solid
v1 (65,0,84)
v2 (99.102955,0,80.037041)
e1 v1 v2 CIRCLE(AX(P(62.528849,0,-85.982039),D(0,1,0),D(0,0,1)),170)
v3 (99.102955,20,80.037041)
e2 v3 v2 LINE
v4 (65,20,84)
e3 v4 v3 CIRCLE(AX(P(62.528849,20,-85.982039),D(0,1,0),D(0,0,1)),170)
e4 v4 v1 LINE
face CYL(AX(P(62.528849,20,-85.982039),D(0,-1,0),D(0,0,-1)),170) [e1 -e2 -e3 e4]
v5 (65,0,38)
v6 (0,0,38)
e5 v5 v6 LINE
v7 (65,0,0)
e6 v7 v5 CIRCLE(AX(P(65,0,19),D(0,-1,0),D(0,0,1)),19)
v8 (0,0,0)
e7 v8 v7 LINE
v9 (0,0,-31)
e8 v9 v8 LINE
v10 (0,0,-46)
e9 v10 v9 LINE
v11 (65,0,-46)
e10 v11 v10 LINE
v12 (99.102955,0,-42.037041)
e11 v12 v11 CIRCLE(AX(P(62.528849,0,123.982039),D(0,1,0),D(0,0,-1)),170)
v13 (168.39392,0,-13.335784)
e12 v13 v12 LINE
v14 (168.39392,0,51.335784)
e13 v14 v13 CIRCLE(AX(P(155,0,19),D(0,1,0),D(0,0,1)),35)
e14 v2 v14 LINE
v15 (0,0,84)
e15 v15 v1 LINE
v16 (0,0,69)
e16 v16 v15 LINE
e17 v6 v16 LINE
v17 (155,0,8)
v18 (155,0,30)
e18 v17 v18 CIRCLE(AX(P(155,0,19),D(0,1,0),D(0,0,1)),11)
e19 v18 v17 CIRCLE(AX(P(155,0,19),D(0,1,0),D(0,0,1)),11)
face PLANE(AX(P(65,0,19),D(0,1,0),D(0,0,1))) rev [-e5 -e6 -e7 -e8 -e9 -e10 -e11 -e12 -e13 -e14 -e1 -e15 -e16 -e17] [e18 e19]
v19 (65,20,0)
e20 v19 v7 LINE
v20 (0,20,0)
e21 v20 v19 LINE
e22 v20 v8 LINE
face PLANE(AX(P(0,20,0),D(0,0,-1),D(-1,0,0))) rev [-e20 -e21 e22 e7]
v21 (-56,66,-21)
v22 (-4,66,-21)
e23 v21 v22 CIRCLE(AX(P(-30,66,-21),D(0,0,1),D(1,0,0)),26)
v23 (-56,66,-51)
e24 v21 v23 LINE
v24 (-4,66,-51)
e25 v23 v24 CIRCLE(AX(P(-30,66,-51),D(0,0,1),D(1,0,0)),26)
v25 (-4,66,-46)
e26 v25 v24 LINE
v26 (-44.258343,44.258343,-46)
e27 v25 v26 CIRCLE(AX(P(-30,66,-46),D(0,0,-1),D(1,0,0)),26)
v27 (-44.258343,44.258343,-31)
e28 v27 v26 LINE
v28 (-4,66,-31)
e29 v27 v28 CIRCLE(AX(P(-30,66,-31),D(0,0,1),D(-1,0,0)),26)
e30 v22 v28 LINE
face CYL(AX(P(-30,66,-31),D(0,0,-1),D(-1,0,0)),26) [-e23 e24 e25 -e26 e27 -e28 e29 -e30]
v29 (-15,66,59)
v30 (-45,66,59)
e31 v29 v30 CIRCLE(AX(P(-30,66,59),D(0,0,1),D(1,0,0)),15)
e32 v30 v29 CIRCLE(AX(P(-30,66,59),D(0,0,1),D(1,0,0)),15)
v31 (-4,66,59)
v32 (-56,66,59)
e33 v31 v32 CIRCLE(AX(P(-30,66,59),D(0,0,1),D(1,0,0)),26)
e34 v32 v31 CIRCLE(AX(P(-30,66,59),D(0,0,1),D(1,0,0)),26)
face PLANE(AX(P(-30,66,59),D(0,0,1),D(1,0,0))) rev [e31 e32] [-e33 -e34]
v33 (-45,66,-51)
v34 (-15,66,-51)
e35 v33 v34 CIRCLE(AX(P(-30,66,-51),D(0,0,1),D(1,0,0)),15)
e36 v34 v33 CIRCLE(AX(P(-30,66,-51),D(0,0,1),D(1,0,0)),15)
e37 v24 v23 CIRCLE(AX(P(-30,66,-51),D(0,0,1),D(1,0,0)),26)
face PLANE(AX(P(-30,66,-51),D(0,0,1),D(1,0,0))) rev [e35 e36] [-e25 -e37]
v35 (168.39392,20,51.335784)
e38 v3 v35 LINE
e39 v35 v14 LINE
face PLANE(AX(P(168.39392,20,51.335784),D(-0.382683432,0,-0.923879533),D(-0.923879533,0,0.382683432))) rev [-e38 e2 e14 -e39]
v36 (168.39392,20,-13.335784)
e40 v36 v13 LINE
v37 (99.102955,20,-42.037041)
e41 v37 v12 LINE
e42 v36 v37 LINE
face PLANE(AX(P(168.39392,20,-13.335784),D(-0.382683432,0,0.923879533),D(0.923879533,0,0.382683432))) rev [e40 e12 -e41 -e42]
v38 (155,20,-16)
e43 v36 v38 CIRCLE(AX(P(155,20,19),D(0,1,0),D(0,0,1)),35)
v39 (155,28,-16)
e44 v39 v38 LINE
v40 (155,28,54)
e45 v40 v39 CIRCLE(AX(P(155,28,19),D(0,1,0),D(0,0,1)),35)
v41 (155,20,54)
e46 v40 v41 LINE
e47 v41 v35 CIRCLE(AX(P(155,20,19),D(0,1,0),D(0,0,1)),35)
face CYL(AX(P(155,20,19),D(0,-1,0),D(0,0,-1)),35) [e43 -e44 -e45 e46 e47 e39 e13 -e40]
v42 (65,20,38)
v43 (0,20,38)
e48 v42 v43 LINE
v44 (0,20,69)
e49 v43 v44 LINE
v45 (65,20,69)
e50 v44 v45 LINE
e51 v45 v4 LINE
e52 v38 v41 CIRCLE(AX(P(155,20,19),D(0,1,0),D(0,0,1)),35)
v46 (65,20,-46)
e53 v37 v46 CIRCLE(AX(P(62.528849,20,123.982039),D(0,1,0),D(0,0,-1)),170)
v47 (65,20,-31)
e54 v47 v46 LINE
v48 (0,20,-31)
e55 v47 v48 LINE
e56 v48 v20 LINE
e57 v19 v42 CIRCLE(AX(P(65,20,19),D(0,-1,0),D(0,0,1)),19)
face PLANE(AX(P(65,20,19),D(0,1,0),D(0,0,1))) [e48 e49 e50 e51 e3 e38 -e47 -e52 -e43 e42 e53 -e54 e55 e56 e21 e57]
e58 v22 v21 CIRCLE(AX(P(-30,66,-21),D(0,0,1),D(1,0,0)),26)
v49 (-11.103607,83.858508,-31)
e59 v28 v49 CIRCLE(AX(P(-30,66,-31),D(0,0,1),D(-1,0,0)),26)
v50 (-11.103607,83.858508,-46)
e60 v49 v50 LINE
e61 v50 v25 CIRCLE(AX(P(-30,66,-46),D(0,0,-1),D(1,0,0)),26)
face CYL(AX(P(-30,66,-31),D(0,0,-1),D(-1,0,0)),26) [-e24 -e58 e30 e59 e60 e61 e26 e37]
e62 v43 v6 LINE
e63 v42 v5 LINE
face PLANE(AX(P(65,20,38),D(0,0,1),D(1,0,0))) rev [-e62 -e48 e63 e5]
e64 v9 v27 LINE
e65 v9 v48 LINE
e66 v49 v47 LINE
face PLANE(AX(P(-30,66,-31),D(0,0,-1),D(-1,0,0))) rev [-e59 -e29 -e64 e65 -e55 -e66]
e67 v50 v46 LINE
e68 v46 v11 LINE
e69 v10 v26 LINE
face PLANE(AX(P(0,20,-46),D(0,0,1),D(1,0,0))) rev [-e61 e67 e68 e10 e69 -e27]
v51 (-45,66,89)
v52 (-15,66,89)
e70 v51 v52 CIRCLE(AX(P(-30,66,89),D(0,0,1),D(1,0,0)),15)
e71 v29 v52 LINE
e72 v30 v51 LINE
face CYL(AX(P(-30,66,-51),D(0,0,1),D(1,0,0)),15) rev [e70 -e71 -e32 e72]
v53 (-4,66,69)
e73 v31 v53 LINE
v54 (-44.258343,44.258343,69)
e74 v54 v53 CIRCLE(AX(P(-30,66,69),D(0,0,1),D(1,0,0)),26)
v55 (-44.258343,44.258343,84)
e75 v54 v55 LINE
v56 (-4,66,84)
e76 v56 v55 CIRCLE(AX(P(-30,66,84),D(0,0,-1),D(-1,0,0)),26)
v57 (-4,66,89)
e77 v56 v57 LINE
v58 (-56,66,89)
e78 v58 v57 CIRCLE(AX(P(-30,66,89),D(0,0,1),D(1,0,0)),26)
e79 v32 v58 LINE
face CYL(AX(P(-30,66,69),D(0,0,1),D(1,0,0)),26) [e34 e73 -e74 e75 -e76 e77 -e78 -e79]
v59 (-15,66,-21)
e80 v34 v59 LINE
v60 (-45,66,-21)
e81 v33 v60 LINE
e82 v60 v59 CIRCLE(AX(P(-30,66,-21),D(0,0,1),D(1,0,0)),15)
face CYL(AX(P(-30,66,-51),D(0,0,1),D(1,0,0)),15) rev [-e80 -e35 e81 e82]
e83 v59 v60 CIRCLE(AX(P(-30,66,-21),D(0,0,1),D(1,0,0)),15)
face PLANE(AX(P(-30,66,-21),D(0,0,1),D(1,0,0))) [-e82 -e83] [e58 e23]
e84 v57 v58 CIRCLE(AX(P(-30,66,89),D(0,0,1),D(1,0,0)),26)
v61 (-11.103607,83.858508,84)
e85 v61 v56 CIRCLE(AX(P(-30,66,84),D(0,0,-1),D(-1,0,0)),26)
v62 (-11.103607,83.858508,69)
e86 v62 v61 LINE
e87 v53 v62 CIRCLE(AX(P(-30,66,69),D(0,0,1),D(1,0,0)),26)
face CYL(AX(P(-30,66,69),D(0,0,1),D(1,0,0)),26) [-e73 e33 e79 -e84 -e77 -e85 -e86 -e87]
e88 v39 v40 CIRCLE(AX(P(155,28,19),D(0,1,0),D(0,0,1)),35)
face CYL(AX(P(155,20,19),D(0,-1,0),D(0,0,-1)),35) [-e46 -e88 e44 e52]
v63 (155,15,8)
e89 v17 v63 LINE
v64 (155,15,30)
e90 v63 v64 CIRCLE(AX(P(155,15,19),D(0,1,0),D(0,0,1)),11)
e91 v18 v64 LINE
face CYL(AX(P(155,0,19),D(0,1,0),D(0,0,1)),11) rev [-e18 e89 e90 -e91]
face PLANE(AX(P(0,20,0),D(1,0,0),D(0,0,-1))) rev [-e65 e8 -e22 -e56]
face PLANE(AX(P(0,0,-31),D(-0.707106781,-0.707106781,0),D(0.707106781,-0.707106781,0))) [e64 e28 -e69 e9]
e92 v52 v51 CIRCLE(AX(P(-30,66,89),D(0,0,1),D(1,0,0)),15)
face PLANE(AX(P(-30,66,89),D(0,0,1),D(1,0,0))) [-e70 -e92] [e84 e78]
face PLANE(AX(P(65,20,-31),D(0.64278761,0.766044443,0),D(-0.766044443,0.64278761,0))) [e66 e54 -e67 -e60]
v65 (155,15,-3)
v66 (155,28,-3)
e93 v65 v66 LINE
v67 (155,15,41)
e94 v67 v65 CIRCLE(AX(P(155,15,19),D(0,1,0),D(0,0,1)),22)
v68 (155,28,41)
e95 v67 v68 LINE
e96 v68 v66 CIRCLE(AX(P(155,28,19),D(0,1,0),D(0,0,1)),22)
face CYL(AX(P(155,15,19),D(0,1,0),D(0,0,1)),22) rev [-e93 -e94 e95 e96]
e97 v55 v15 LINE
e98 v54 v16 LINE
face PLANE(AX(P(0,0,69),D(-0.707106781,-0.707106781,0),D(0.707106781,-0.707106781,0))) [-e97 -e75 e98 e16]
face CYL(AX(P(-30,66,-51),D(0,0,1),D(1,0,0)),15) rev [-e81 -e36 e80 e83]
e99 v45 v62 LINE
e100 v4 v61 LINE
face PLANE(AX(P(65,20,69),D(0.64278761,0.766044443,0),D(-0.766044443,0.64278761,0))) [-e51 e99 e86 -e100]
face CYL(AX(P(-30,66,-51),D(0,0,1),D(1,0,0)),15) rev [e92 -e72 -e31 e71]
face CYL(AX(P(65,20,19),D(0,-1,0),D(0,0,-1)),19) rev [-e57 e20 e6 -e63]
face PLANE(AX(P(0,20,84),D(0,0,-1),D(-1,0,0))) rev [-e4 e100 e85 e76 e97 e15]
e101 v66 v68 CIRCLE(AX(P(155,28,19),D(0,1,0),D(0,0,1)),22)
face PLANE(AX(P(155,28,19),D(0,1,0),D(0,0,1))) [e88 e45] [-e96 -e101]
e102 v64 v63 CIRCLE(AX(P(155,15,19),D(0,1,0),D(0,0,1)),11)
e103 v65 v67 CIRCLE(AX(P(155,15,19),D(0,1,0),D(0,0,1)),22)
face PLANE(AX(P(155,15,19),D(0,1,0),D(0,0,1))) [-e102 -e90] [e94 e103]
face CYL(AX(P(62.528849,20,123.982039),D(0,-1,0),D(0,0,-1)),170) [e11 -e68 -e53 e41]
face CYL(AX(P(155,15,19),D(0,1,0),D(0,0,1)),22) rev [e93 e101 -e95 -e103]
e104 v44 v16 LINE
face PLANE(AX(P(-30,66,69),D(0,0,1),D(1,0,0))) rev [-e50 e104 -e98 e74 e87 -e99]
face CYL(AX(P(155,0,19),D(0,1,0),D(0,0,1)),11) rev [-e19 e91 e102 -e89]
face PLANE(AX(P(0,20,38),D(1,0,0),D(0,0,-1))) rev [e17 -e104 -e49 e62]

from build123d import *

# Parameters (mm, degrees)
BASE_PLATE_DEPTH           = 20
PIVOT_BOSS_SKETCH_R        = 35
PIVOT_BOSS_70_DEPTH        = 8
ARM_WEB_1_DEPTH            = 15
ARM_START                  = -15
ARM_WEB_2_DEPTH            = 15
LUG_START                  = 30
LUG_BOSS_1_SKETCH_R        = 26
LUG_BOSS_1_52_DEPTH        = 30
LUG_BOSS_2_SKETCH_R        = 26
LUG_BOSS_2_52_DEPTH        = 30
LUG_BORE_SKETCH_R          = 15
LUG_BORE_30_DEPTH          = 254.306139
PIVOT_COUNTERBORE_SKETCH_R = 22
PIVOT_COUNTERBORE_44_DEPTH = 13
PIVOT_HOLE_SKETCH_R        = 11
PIVOT_HOLE_22_DEPTH        = 224.494966


with BuildPart() as part:
    # Base Plate Sketch → Base Plate (new body)
    with BuildSketch(Plane(origin=(0, 0, 0), x_dir=(1, 0, 0), z_dir=(0, 1, 0))):
        with BuildLine():
            Line((0, 0), (0, 46))
            Line((0, 46), (65, 46))
            ThreePointArc((65, 46), (82.151777, 44.881636), (99.102955, 42.037041))
            Line((99.102955, 42.037041), (168.39392, 13.335784))
            ThreePointArc((168.39392, 13.335784), (190, -19), (168.39392, -51.335784))
            Line((168.39392, -51.335784), (99.102955, -80.037041))
            ThreePointArc((99.102955, -80.037041), (82.151777, -82.881636), (65, -84))
            Line((65, -84), (0, -84))
            Line((0, -84), (0, -38))
            Line((0, -38), (65, -38))
            ThreePointArc((65, -38), (84, -19), (65, 0))
            Line((65, 0), (0, 0))
        make_face()
    extrude(amount=BASE_PLATE_DEPTH)

    # Pivot Boss Sketch → Pivot Boss Ø70 (add)
    with BuildSketch(Plane(origin=(0, 20, 0), x_dir=(1, 0, 0), z_dir=(0, 1, 0))):
        with Locations(Location((155, -19, 0), (0, 0, 67.5))):
            Circle(PIVOT_BOSS_SKETCH_R)
    extrude(amount=PIVOT_BOSS_70_DEPTH)

    # Arm Web 1 Sketch → Arm Web 1 (add)
    with BuildSketch(Plane.XY.offset(84)):
        with BuildLine():
            Line((0, 0), (-44.258343, 44.258343))
            ThreePointArc((-44.258343, 44.258343), (-49.935425, 82.690681), (-11.103607, 83.858508))
            Line((-11.103607, 83.858508), (65, 20))
            Line((65, 20), (65, 0))
            Line((65, 0), (0, 0))
        make_face()
    extrude(amount=-ARM_WEB_1_DEPTH)

    # Arm Web 2 Sketch → Arm Web 2 (add)
    with BuildSketch(Plane(origin=(0, 0, -46), x_dir=(-1, 0, 0), z_dir=(0, 0, -1)).offset(ARM_START)):
        with BuildLine():
            Line((-65, 20), (-65, 0))
            Line((-65, 0), (0, 0))
            Line((0, 0), (44.258343, 44.258343))
            ThreePointArc((44.258343, 44.258343), (49.935425, 82.690681), (11.103607, 83.858508))
            Line((11.103607, 83.858508), (-65, 20))
        make_face()
    extrude(amount=ARM_WEB_2_DEPTH)

    # Lug Boss 1 Sketch → Lug Boss 1 Ø52 (add)
    with BuildSketch(Plane.XY.offset(-51).offset(LUG_START)):
        with Locations((-30, 66)):
            Circle(LUG_BOSS_1_SKETCH_R)
    extrude(amount=-LUG_BOSS_1_52_DEPTH)

    # Lug Boss 2 Sketch → Lug Boss 2 Ø52 (add)
    with BuildSketch(Plane.XY.offset(89)):
        with Locations((-30, 66)):
            Circle(LUG_BOSS_2_SKETCH_R)
    extrude(amount=-LUG_BOSS_2_52_DEPTH)

    # Lug Bore Sketch → Lug Bore Ø30 (cut, through all)
    with BuildSketch(Plane.XY.offset(89)):
        with Locations((-30, 66)):
            Circle(LUG_BORE_SKETCH_R)
    extrude(amount=-LUG_BORE_30_DEPTH, mode=Mode.SUBTRACT)

    # Pivot Counterbore Sketch → Pivot Counterbore Ø44 (cut)
    with BuildSketch(Plane(origin=(0, 28, 0), x_dir=(1, 0, 0), z_dir=(0, 1, 0))):
        with Locations(Location((155, -19, 0), (0, 0, 270))):
            Circle(PIVOT_COUNTERBORE_SKETCH_R)
    extrude(amount=-PIVOT_COUNTERBORE_44_DEPTH, mode=Mode.SUBTRACT)

    # Pivot Hole Sketch → Pivot Hole Ø22 (cut, through all)
    with BuildSketch(Plane(origin=(0, 15, 0), x_dir=(1, 0, 0), z_dir=(0, 1, 0))):
        with Locations(Location((155, -19, 0), (0, 0, 270))):
            Circle(PIVOT_HOLE_SKETCH_R)
    extrude(amount=-PIVOT_HOLE_22_DEPTH, mode=Mode.SUBTRACT)


solid = part.part
